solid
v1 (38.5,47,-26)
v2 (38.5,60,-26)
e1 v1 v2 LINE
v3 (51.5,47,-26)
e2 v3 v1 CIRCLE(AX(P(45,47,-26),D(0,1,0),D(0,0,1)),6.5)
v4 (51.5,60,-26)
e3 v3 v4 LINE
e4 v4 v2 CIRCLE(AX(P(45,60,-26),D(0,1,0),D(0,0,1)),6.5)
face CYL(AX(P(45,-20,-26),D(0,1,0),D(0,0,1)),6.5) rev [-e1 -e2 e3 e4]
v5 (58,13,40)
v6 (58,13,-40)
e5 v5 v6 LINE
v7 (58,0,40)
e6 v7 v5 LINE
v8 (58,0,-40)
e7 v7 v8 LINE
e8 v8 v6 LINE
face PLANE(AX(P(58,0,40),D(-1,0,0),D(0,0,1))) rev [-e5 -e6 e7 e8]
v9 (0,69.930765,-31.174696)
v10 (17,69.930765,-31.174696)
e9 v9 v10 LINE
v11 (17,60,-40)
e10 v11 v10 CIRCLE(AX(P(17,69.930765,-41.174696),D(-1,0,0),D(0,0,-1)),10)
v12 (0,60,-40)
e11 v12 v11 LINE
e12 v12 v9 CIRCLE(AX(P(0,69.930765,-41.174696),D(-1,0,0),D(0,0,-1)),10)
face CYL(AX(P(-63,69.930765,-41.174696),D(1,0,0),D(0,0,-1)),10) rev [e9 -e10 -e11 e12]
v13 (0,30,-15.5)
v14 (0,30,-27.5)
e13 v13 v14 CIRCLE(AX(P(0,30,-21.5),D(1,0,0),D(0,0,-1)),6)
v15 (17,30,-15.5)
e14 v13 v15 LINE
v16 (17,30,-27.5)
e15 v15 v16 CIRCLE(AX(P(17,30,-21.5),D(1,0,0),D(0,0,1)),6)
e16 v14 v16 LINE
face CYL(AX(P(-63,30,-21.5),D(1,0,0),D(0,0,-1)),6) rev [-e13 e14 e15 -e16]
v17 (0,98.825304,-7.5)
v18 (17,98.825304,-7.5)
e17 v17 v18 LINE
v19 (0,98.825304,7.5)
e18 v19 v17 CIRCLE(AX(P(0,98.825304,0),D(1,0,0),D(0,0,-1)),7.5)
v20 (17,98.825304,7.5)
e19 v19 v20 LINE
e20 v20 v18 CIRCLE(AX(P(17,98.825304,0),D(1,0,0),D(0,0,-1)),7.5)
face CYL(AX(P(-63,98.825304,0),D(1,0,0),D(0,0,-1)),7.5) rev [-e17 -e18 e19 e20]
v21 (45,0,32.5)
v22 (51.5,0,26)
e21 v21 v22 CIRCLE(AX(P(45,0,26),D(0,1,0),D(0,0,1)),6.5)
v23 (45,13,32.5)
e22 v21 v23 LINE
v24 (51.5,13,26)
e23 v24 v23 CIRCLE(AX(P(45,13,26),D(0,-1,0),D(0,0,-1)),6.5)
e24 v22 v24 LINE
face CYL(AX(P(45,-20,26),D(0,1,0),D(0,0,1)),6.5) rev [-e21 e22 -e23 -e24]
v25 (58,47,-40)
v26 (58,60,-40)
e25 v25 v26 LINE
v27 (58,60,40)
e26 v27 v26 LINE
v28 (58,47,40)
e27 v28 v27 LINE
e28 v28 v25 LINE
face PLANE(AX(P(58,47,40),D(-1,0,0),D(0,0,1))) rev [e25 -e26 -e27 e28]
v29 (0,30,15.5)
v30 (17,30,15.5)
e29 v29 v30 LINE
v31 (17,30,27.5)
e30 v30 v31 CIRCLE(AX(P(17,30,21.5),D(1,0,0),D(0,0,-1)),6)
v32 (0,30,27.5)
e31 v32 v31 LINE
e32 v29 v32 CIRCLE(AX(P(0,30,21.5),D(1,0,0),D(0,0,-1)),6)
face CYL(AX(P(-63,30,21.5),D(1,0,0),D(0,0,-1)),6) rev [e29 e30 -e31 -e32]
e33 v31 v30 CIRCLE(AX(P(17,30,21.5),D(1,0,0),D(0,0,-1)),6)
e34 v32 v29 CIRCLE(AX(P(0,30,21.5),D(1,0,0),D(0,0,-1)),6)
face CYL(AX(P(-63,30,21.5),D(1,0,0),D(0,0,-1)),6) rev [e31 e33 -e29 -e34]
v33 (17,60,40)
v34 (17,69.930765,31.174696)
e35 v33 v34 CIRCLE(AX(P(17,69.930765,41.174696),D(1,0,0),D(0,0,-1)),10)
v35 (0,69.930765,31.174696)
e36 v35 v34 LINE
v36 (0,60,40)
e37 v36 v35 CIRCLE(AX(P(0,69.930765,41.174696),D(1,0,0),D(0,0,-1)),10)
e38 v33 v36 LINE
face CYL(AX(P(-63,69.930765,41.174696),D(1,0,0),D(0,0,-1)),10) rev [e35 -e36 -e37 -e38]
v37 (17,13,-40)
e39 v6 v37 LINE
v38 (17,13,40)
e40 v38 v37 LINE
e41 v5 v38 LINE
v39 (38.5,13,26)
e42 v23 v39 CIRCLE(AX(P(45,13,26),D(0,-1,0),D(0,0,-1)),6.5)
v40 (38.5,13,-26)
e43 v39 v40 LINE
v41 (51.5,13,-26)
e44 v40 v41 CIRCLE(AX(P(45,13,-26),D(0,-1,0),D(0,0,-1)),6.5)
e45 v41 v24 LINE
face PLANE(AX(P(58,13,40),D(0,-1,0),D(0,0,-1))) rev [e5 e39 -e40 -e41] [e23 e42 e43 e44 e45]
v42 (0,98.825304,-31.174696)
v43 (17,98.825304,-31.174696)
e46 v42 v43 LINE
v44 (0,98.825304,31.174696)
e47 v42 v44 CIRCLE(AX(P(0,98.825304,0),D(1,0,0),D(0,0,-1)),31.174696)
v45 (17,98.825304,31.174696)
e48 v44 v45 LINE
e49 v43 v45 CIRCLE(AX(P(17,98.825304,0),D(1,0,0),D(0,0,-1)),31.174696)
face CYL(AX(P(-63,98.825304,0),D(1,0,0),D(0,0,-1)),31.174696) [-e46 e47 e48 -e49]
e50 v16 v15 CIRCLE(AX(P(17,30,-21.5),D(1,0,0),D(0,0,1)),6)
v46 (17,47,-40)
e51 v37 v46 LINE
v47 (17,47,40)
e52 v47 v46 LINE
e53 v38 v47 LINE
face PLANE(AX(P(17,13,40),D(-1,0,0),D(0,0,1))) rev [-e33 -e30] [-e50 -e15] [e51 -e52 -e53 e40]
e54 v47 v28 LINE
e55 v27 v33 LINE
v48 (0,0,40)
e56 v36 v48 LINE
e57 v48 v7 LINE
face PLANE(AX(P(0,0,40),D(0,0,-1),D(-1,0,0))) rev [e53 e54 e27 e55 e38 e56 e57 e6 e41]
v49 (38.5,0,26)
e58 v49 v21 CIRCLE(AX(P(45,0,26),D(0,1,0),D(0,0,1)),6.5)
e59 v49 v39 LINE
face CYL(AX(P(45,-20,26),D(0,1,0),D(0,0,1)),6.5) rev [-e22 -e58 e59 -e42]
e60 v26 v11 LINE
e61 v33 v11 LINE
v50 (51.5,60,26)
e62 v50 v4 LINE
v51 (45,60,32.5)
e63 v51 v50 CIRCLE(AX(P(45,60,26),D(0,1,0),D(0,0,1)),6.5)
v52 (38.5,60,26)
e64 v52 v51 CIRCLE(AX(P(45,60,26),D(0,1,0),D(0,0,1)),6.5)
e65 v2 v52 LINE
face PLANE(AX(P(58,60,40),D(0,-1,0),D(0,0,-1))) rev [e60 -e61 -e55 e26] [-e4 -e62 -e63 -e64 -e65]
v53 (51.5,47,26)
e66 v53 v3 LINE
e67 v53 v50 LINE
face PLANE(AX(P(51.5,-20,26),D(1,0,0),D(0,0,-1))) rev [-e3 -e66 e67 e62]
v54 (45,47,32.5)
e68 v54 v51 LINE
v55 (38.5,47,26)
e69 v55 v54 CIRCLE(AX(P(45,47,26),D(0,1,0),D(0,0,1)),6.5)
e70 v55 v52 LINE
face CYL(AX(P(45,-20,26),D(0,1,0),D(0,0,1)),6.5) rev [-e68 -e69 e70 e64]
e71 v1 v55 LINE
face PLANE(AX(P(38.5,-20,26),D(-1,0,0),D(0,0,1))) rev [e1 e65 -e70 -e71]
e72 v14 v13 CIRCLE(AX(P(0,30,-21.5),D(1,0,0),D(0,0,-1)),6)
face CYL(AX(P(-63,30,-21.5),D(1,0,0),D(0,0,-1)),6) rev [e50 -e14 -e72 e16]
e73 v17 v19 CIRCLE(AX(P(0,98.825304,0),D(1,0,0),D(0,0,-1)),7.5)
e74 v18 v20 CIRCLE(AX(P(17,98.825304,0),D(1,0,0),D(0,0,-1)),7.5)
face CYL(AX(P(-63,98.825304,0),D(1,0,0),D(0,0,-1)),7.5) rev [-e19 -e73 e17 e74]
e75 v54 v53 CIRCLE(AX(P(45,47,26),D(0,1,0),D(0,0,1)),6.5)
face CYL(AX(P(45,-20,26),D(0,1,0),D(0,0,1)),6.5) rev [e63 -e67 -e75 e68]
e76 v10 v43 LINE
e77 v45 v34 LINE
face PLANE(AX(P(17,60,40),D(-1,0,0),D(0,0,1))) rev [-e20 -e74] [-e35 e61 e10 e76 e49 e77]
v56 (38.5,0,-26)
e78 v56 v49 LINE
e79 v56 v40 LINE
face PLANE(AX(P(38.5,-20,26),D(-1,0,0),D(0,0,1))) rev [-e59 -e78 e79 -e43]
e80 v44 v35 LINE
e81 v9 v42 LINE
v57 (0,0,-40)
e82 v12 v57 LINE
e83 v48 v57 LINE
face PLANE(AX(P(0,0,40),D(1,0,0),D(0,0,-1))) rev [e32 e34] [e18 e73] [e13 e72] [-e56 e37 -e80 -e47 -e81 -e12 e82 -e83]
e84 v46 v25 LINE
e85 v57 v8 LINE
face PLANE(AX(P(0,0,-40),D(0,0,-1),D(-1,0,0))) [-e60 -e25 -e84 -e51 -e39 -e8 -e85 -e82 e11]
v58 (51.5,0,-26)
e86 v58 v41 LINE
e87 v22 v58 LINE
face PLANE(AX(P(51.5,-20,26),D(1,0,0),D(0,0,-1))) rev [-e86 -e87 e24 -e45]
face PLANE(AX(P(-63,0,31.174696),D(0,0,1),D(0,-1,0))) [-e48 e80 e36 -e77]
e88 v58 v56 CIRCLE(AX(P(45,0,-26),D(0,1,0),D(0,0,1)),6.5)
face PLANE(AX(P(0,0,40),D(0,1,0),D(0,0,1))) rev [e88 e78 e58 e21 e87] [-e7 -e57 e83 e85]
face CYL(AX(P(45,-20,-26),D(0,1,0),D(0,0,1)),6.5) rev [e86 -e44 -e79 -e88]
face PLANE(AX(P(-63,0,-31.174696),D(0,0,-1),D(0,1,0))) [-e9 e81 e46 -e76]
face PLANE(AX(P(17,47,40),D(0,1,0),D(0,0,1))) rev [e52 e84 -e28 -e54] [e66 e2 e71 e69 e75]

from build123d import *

# Parameters (mm, degrees)
BRACKET_BODY_DEPTH    = 40
ROUNDED_LUG_CUT_DEPTH = 80
PIN_HOLE_SKETCH_R     = 7.5
PIN_HOLE_15_DEPTH     = 80
FORK_GAP_SKETCH_R     = 6
FORK_GAP_12MM_DEPTH   = 80
ARM_SLOTS_2X6_5_DEPTH = 80


with BuildPart() as part:
    # Bracket Profile Sketch → Bracket Body (new, symmetric)
    with BuildSketch(Plane.XY):
        Polygon((0, 0), (58, 0), (58, 13), (17, 13), (17, 47), (58, 47), (58, 60), (17, 60), (17, 130), (0, 130), align=None)
    extrude(amount=BRACKET_BODY_DEPTH, both=True)

    # Lug Shape Sketch → Rounded Lug Cut (cut)
    with BuildSketch(Plane(origin=(17, 0, 0), x_dir=(0, 0, -1), z_dir=(1, 0, 0))):
        with BuildLine():
            Line((40, 130), (9.4e-08, 130))
            ThreePointArc((9.4e-08, 130), (22.043839272, 120.869142787), (31.174696418, 98.825303582))
            Line((31.174696418, 98.825303582), (31.174696418, 69.93076474))
            ThreePointArc((31.174696418, 69.93076474), (33.699839758, 63.287985359), (40, 60))
            Line((40, 60), (40, 130))
        make_face()
        with BuildLine():
            Line((-31.174696418, 69.93076474), (-31.174696418, 98.825303582))
            ThreePointArc((-31.174696418, 98.825303582), (-22.043839205, 120.869142854), (9.4e-08, 130))
            Line((9.4e-08, 130), (-40, 130))
            Line((-40, 130), (-40, 60))
            ThreePointArc((-40, 60), (-33.699839758, 63.287985359), (-31.174696418, 69.93076474))
        make_face()
    extrude(amount=-ROUNDED_LUG_CUT_DEPTH, mode=Mode.SUBTRACT)

    # Pin Hole Sketch → Pin Hole Ø15 (cut)
    with BuildSketch(Plane(origin=(17, 0, 0), x_dir=(0, 0, -1), z_dir=(1, 0, 0))):
        with Locations((0, 98.825303582)):
            Circle(PIN_HOLE_SKETCH_R)
    extrude(amount=-PIN_HOLE_15_DEPTH, mode=Mode.SUBTRACT)

    # Fork Gap Sketch → Fork Gap 12mm (cut)
    with BuildSketch(Plane(origin=(17, 0, 0), x_dir=(0, 0, -1), z_dir=(1, 0, 0))):
        with Locations((-21.5, 30)):
            Circle(FORK_GAP_SKETCH_R)
        with Locations((21.5, 30)):
            Circle(FORK_GAP_SKETCH_R)
    extrude(amount=-FORK_GAP_12MM_DEPTH, mode=Mode.SUBTRACT)

    # Arm Slots Sketch → Arm Slots 2x6.5 (cut)
    with BuildSketch(Plane(origin=(0, 60, 0), x_dir=(1, 0, 0), z_dir=(0, 1, 0))):
        with BuildLine():
            Line((38.5, -26), (38.5, 26))
            ThreePointArc((38.5, 26), (45, 32.5), (51.5, 26))
            Line((51.5, 26), (51.5, -26))
            ThreePointArc((51.5, -26), (45, -32.5), (38.5, -26))
        make_face()
    extrude(amount=-ARM_SLOTS_2X6_5_DEPTH, mode=Mode.SUBTRACT)


solid = part.part
